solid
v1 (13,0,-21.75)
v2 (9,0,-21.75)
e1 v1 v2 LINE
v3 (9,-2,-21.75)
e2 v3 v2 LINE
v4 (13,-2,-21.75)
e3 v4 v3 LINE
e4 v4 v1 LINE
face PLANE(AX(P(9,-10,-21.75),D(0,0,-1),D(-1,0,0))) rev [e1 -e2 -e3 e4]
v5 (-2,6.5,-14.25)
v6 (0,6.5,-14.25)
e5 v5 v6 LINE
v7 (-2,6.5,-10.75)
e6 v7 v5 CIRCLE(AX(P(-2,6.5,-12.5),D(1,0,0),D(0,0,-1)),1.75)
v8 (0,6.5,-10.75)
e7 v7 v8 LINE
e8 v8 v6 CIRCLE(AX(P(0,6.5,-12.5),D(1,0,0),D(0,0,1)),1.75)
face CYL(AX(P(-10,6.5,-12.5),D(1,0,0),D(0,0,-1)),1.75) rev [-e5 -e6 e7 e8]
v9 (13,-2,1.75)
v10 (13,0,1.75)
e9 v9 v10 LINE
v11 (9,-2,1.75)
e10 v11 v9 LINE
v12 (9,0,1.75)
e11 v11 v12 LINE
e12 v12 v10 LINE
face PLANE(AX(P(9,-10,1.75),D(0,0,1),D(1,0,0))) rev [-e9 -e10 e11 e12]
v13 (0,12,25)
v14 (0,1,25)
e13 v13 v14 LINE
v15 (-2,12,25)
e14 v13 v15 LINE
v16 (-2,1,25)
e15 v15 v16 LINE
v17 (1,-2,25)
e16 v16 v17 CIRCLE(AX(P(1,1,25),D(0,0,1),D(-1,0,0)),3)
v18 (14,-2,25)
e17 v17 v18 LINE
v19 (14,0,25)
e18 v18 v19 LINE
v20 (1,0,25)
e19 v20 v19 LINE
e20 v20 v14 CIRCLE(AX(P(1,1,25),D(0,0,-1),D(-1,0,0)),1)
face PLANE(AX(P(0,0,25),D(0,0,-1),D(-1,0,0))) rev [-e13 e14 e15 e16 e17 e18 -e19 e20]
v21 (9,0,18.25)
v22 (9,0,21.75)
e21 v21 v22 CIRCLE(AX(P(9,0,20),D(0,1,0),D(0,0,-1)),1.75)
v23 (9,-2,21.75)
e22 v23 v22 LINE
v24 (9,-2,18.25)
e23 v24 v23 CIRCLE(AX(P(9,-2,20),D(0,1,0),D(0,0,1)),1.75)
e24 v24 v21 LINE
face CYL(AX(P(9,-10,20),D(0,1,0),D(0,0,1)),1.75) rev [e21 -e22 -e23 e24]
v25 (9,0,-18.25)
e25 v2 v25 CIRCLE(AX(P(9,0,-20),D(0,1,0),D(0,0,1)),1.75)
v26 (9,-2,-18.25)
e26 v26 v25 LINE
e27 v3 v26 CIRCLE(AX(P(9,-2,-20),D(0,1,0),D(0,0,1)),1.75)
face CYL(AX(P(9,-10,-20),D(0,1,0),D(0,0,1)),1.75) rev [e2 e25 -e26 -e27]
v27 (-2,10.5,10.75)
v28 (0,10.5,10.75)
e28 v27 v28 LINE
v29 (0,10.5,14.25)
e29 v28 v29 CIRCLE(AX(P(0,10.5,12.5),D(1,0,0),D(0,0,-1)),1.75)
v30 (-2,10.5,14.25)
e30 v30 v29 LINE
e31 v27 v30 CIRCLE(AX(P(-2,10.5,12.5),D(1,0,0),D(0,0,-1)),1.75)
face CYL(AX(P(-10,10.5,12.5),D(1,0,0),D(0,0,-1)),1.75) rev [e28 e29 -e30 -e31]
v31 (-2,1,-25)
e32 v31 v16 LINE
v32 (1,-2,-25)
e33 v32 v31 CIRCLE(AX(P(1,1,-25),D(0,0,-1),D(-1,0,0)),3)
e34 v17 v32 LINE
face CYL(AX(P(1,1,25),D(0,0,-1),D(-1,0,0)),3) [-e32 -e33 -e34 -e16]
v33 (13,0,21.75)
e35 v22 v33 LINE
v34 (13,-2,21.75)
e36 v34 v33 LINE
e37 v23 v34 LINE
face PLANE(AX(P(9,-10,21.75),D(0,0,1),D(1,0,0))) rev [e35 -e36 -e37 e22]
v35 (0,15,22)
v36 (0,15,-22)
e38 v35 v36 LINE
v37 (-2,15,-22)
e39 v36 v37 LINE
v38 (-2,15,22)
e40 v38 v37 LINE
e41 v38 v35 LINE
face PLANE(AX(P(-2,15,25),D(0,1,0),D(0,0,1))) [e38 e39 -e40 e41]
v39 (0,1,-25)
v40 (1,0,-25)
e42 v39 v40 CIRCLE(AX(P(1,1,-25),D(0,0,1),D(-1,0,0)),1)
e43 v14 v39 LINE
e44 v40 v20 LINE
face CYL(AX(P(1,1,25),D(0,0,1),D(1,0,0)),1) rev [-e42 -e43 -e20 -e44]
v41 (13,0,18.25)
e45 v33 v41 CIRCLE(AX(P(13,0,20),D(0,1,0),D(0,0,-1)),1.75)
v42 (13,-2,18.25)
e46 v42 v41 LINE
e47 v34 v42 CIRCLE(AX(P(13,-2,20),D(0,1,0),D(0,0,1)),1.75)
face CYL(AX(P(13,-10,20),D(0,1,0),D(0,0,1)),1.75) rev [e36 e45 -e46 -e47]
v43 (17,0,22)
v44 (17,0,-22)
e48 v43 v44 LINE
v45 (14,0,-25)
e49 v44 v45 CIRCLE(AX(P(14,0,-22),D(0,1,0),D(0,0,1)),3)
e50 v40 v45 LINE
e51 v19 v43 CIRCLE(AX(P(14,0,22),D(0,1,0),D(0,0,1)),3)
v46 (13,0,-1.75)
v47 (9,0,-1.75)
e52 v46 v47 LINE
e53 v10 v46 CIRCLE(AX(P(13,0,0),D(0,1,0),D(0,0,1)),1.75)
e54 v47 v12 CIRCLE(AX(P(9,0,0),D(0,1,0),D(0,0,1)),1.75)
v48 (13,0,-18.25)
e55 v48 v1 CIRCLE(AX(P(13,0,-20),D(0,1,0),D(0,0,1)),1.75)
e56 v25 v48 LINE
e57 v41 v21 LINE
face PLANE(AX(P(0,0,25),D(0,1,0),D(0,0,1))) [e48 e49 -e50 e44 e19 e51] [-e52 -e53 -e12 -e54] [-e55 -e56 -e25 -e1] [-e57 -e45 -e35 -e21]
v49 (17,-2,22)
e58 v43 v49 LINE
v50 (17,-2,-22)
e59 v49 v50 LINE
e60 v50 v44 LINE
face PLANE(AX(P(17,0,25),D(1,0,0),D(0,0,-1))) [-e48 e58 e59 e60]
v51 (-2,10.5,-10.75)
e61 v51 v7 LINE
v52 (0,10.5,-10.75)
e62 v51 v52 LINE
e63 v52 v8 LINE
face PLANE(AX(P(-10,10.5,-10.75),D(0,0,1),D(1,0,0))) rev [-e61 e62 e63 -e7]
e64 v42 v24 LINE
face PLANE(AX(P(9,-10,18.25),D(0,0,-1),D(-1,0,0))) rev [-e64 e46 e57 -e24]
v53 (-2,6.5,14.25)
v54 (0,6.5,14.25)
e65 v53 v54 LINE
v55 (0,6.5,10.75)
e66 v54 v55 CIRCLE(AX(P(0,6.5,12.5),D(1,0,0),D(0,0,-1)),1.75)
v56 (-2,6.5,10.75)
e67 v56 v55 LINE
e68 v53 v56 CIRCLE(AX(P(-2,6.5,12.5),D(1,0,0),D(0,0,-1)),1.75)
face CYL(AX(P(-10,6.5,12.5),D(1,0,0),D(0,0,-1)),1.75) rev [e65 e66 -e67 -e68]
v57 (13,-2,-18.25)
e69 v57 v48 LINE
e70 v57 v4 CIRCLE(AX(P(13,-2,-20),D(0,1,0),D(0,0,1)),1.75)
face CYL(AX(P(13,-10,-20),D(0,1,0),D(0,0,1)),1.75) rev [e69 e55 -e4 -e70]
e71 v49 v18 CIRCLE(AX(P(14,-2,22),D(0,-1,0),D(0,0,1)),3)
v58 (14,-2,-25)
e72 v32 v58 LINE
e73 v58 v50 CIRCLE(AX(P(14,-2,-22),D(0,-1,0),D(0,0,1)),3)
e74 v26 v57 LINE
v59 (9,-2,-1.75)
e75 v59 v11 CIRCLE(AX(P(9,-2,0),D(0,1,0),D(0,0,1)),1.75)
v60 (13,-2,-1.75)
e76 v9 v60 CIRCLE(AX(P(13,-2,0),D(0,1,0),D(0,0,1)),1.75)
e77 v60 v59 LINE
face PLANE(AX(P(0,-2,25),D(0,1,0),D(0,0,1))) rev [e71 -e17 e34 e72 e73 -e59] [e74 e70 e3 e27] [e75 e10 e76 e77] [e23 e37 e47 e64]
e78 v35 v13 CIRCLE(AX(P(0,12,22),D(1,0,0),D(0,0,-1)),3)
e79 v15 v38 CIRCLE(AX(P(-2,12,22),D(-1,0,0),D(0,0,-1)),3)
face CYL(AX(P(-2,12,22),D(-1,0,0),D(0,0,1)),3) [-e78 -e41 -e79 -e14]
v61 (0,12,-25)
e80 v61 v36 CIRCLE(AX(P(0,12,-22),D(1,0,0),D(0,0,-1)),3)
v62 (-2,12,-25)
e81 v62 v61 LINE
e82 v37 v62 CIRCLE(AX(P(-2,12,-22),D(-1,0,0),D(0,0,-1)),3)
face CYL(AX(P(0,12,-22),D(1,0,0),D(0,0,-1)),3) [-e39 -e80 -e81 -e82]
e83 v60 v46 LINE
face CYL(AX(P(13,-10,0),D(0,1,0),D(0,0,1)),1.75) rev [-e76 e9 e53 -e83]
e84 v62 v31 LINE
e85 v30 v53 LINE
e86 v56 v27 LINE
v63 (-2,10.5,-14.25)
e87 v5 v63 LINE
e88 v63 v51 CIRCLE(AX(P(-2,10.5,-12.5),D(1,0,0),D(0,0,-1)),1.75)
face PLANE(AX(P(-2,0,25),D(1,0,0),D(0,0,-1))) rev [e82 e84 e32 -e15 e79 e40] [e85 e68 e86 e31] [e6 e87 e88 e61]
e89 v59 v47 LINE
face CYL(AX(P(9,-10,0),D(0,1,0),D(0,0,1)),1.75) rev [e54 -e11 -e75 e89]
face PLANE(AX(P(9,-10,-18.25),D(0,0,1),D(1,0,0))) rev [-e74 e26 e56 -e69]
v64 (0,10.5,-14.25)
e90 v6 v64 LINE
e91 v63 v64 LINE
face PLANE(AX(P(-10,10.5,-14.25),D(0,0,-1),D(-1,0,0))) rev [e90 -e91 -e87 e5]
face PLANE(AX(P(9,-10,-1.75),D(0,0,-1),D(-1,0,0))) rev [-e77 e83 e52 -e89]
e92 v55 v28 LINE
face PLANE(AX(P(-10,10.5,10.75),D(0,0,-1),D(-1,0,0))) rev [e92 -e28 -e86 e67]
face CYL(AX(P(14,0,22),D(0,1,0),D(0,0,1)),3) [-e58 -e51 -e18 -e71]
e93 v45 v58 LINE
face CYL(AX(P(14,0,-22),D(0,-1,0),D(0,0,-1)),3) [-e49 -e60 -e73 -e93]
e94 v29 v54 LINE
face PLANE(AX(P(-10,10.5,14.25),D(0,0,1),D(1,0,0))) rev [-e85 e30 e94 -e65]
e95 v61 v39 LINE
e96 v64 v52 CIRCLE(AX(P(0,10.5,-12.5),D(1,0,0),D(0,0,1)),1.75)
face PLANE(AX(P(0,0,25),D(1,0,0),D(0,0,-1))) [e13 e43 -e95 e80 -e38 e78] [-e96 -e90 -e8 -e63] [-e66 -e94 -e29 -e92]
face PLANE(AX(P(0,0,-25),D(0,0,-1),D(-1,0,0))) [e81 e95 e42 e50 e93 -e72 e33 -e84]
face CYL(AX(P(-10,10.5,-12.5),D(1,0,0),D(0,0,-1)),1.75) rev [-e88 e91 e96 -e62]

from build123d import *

# Parameters (mm, degrees)
EXTRUDE_1_DEPTH     = 25
CUT_EXTRUDE_1_DEPTH = 10
CUT_EXTRUDE_2_DEPTH = 10
FILLET_1_R          = 3
FILLET_2_R          = 1
FILLET_3_R          = 3


with BuildPart() as part:
    # 草图9 → 拉伸-薄壁1 (new, symmetric)
    with BuildSketch(Plane.XY):
        Polygon((17, 0), (0, 0), (0, 15), (-2, 15), (-2, -2), (17, -2), align=None)
    extrude(amount=EXTRUDE_1_DEPTH, both=True)

    # 草图10 → 切除-拉伸1 (cut)
    with BuildSketch(Plane(origin=(0, 0, 0), x_dir=(1, 0, 0), z_dir=(0, 1, 0))):
        with BuildLine():
            Line((9, 21.75), (13, 21.75))
            ThreePointArc((13, 21.75), (14.75, 20), (13, 18.25))
            Line((13, 18.25), (9, 18.25))
            ThreePointArc((9, 18.25), (7.25, 20), (9, 21.75))
        make_face()
        with BuildLine():
            Line((9, -21.75), (13, -21.75))
            ThreePointArc((13, -21.75), (14.75, -20), (13, -18.25))
            Line((13, -18.25), (9, -18.25))
            ThreePointArc((9, -18.25), (7.25, -20), (9, -21.75))
        make_face()
        with BuildLine():
            Line((9, 1.75), (13, 1.75))
            ThreePointArc((13, 1.75), (14.75, 0), (13, -1.75))
            Line((13, -1.75), (9, -1.75))
            ThreePointArc((9, -1.75), (7.25, 0), (9, 1.75))
        make_face()
    extrude(amount=-CUT_EXTRUDE_1_DEPTH, mode=Mode.SUBTRACT)

    # 草图11 → 切除-拉伸2 (cut)
    with BuildSketch(Plane(origin=(0, 0, 0), x_dir=(0, 0, -1), z_dir=(1, 0, 0))):
        with BuildLine():
            Line((-10.75, 10.5), (-10.75, 6.5))
            ThreePointArc((-10.75, 6.5), (-12.5, 4.75), (-14.25, 6.5))
            Line((-14.25, 6.5), (-14.25, 10.5))
            ThreePointArc((-14.25, 10.5), (-12.5, 12.25), (-10.75, 10.5))
        make_face()
        with BuildLine():
            Line((10.75, 10.5), (10.75, 6.5))
            ThreePointArc((10.75, 6.5), (12.5, 4.75), (14.25, 6.5))
            Line((14.25, 6.5), (14.25, 10.5))
            ThreePointArc((14.25, 10.5), (12.5, 12.25), (10.75, 10.5))
        make_face()
    extrude(amount=-CUT_EXTRUDE_2_DEPTH, mode=Mode.SUBTRACT)

    # 圆角1
    fillet_1_edges = [part.edges().sort_by_distance(p)[0] for p in [
        (-1, 15, 25),
        (-1, 15, -25),
        (17, -1, -25),
        (17, -1, 25),
    ]]
    fillet(fillet_1_edges, radius=FILLET_1_R)

    # 圆角2
    fillet_2_edges = [part.edges().sort_by_distance(p)[0] for p in [
        (0, 0, 0),
    ]]
    fillet(fillet_2_edges, radius=FILLET_2_R)

    # 圆角3
    fillet_3_edges = [part.edges().sort_by_distance(p)[0] for p in [
        (-2, -2, 0),
    ]]
    fillet(fillet_3_edges, radius=FILLET_3_R)


solid = part.part
